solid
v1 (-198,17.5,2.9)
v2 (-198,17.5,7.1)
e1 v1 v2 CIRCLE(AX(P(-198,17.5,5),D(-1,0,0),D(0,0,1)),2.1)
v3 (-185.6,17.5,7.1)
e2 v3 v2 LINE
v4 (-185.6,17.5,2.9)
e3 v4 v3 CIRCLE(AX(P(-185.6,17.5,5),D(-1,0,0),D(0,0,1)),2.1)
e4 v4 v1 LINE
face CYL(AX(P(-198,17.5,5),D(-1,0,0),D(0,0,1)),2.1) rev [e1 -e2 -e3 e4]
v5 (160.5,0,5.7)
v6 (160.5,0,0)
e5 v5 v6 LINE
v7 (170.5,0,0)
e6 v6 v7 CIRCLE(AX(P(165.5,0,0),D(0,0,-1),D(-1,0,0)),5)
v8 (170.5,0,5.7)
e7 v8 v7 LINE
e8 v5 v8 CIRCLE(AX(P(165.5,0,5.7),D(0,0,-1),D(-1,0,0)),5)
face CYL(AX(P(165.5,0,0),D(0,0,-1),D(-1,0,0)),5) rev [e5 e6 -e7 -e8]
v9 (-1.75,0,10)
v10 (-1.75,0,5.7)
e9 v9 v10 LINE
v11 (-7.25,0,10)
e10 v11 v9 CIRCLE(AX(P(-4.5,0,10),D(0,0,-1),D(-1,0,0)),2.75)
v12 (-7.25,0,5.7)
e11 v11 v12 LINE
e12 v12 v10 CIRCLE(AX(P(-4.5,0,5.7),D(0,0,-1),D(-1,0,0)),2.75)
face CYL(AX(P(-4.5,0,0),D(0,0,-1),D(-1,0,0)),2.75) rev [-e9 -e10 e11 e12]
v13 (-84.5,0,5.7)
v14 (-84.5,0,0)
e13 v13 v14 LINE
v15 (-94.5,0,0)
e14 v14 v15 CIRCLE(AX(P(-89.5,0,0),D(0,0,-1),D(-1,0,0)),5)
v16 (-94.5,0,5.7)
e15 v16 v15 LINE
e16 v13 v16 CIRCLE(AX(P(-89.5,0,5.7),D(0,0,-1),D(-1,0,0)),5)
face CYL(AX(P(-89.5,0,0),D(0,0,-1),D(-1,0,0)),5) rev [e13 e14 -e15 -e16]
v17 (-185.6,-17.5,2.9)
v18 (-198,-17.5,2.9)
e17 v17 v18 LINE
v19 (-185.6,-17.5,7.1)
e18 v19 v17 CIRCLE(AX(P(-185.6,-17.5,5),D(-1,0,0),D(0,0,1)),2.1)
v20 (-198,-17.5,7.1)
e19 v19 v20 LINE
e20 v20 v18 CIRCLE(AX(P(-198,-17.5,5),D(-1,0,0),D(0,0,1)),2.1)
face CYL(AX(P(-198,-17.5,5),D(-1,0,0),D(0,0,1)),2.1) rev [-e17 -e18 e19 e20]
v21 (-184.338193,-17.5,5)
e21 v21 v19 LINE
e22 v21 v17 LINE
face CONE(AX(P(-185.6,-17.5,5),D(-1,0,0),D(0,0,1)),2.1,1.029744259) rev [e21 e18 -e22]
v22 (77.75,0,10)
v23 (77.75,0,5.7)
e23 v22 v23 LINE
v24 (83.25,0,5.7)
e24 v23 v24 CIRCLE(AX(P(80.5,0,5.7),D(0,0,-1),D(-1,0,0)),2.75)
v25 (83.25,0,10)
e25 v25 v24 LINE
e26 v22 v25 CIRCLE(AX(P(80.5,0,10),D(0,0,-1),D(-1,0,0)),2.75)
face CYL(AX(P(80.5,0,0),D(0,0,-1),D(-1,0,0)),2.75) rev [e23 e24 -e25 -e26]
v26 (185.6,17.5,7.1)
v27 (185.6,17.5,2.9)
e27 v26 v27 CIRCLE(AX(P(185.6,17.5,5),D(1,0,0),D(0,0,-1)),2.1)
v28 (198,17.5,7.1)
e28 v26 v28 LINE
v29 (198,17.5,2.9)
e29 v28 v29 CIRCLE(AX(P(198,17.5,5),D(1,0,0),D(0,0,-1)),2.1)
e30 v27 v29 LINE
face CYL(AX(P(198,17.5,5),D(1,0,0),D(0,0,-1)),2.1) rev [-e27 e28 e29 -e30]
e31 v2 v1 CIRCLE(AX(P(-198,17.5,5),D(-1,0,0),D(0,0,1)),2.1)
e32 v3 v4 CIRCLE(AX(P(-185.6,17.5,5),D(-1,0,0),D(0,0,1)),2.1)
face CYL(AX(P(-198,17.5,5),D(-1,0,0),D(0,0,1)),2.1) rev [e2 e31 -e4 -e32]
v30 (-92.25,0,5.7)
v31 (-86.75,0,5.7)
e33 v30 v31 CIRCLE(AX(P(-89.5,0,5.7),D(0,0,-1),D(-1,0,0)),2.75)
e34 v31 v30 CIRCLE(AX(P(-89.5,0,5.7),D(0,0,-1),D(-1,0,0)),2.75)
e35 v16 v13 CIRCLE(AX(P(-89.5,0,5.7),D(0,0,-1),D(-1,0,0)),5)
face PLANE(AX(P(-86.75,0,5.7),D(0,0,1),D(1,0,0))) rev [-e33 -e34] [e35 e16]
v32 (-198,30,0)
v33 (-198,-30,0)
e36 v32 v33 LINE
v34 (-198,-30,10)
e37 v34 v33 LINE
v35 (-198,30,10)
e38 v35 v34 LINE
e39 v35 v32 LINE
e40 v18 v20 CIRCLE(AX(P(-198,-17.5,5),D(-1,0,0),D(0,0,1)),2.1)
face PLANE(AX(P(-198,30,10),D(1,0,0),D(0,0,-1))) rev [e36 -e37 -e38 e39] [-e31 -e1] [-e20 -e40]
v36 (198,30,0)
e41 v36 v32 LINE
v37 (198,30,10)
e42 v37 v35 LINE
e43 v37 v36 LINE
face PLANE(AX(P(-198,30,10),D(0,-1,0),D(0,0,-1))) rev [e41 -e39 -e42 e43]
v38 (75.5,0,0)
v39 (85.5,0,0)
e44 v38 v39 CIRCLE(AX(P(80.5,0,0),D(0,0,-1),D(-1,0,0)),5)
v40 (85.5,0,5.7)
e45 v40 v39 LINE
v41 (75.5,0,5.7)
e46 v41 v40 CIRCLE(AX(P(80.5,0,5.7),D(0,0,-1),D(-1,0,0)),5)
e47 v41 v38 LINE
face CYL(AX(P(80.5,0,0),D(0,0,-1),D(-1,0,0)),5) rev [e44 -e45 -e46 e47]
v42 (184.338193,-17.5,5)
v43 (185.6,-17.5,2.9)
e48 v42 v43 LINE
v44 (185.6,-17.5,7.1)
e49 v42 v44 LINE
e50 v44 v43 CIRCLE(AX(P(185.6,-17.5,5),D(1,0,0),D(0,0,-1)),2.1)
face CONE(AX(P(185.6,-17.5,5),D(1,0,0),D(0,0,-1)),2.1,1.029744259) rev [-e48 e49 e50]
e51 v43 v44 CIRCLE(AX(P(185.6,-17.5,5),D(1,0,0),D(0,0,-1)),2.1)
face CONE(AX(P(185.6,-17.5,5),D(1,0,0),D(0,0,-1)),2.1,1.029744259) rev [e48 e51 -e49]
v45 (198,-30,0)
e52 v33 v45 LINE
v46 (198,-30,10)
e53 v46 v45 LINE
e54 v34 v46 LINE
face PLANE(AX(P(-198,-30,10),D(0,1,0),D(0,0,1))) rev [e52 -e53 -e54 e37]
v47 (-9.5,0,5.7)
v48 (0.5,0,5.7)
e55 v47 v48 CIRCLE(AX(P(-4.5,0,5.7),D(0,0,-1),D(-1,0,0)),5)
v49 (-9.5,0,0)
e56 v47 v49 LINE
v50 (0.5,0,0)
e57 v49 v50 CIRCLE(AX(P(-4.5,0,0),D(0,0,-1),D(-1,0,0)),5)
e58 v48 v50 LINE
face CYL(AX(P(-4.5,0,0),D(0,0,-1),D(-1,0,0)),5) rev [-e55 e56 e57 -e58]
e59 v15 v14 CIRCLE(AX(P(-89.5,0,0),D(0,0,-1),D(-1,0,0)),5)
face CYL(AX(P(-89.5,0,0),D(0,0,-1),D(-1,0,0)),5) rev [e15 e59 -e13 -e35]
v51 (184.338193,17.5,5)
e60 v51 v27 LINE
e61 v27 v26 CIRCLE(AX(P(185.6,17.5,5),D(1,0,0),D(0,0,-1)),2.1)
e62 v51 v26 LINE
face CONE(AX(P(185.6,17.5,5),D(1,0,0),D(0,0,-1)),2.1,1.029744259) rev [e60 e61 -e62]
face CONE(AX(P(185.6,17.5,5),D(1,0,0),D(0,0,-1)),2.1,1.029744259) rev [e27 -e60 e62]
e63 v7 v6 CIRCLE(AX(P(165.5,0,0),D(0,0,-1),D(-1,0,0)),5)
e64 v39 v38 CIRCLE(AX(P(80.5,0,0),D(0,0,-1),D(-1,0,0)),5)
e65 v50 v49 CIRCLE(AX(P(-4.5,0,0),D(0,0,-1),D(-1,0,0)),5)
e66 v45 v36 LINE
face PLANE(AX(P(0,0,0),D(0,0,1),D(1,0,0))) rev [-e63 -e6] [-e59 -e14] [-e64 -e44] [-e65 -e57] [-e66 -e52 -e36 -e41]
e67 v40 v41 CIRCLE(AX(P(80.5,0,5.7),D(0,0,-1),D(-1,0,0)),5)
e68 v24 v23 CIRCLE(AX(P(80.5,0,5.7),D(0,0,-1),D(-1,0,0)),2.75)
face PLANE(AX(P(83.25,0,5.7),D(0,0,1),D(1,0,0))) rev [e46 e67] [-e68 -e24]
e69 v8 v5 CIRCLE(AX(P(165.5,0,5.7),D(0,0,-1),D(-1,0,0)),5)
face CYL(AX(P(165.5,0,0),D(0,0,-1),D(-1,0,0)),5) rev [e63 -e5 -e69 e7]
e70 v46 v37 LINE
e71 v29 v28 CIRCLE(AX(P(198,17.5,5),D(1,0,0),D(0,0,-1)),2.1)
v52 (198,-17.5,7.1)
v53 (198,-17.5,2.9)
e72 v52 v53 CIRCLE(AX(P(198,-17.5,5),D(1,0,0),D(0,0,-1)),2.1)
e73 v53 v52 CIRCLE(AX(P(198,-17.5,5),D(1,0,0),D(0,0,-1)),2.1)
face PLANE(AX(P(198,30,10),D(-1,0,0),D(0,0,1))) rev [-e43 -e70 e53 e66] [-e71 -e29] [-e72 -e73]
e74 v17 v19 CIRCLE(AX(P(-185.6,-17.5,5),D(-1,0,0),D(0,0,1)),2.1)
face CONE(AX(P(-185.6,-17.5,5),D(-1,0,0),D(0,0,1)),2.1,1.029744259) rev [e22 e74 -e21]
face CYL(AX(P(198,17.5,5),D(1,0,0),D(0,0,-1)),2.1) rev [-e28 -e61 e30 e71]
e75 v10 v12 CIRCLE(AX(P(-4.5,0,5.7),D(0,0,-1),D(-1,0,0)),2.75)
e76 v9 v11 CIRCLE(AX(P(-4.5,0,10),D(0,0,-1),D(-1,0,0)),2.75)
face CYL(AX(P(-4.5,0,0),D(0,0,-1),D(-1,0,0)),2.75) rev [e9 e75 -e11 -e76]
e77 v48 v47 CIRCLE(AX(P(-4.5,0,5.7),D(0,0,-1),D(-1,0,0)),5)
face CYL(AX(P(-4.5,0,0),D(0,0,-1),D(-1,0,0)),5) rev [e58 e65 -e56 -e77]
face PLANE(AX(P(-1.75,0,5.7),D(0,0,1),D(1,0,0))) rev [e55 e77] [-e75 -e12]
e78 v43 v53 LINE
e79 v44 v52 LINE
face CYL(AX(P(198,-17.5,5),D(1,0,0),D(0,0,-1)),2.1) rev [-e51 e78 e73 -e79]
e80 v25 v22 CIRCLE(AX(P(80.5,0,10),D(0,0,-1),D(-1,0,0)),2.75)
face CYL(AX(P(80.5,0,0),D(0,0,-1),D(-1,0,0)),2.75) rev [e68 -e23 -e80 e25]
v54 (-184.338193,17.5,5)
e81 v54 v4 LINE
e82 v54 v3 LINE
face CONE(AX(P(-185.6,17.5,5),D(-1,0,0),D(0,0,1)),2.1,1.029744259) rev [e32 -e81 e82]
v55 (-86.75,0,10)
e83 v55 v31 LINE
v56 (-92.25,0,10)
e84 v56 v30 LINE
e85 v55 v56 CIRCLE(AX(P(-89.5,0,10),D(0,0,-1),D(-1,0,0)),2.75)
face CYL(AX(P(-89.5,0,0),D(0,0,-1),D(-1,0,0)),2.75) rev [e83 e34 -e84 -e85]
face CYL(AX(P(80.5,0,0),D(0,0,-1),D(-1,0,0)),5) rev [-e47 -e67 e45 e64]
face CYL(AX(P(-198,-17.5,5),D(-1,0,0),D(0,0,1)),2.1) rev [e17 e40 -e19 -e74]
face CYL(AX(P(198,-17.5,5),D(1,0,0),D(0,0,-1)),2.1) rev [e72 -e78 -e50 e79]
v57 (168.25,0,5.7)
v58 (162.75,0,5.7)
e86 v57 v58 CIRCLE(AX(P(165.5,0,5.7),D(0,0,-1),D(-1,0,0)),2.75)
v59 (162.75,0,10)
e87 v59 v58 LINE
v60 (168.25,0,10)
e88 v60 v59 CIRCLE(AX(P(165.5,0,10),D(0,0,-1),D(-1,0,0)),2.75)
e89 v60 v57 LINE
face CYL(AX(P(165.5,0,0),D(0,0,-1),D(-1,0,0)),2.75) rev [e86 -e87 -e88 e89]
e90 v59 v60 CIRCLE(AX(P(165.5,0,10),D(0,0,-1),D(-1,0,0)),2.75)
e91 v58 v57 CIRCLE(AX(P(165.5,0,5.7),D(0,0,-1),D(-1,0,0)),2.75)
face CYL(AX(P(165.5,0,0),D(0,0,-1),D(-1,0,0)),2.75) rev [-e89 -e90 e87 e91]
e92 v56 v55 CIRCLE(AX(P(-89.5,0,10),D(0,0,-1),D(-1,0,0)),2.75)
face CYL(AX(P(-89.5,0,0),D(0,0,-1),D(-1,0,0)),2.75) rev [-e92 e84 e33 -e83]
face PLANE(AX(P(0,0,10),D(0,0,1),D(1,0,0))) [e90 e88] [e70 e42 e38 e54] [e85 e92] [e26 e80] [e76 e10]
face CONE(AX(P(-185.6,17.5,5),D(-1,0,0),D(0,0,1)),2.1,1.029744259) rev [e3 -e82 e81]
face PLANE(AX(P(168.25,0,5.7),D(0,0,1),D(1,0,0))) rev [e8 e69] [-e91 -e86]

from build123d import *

# Parameters (mm, degrees)
SKETCH1_W                                            = 396
SKETCH1_H                                            = 60
BOSS_EXTRUDE1_DEPTH                                  = 10
HOLE_SIZE_PER_SOCKET_HEAD_CAP_SCREW_TYPE_D           = 5.5
HOLE_SIZE_PER_SOCKET_HEAD_CAP_SCREW_TYPE_CBORE_D     = 10
HOLE_SIZE_PER_SOCKET_HEAD_CAP_SCREW_TYPE_CBORE_DEPTH = 5.7
M5_TAPPED_HOLE1_AT_2_COUNT                           = 2
M5_TAPPED_HOLE1_AT_2_PITCH                           = 35


with BuildPart() as part:
    # Sketch1 → Boss-Extrude1 (new body)
    with BuildSketch(Plane.XY):
        Rectangle(SKETCH1_W, SKETCH1_H)
    extrude(amount=BOSS_EXTRUDE1_DEPTH)

    # Hole size per socket head cap screw type 1 (through all)
    with Locations(Plane(origin=(0, 0, 0), x_dir=(-1, 0, 0), z_dir=(0, 0, -1))):
        with Locations((89.5, 0), (4.5, 0), (-80.5, 0), (-165.5, 0)):
            CounterBoreHole(HOLE_SIZE_PER_SOCKET_HEAD_CAP_SCREW_TYPE_D / 2, HOLE_SIZE_PER_SOCKET_HEAD_CAP_SCREW_TYPE_CBORE_D / 2, HOLE_SIZE_PER_SOCKET_HEAD_CAP_SCREW_TYPE_CBORE_DEPTH)

    # Sketch4 → M5 Tapped Hole1 (revolve, cut)
    with BuildSketch(Plane(origin=(-198, 17.5, 5), x_dir=(0, 0, 1), z_dir=(0, 1, 0))):
        Polygon((0, 0), (0, 13.6618073), (2.1, 12.4), (2.1, 0), align=None)
    m5_tapped_hole1 = revolve(axis=Axis((-204.35, 17.5, 5), (1, 0, 0)), mode=Mode.SUBTRACT)

    # M5 Tapped Hole1 at 2: M5 Tapped Hole1 ×2
    with Locations(*[(0, -i * M5_TAPPED_HOLE1_AT_2_PITCH, 0) for i in range(1, M5_TAPPED_HOLE1_AT_2_COUNT)]):
        add(m5_tapped_hole1, mode=Mode.SUBTRACT)

    # Mirror1: M5 Tapped Hole1 across plane
    add(m5_tapped_hole1.mirror(Plane(origin=(0, 0, 0), x_dir=(0, 0, 1), z_dir=(1, 0, 0))), mode=Mode.SUBTRACT)

    # Mirror1 copy 1 sketch → Mirror1 copy 1 (revolve, cut)
    with BuildSketch(Plane(origin=(198, -17.5, 5), x_dir=(0, 0, 1), z_dir=(0, 1, 0))):
        Polygon((0, 0), (0, -13.6618073), (2.1, -12.4), (2.1, 0), align=None)
    revolve(axis=Axis((204.35, -17.5, 5), (1, 0, 0)), mode=Mode.SUBTRACT)


solid = part.part
